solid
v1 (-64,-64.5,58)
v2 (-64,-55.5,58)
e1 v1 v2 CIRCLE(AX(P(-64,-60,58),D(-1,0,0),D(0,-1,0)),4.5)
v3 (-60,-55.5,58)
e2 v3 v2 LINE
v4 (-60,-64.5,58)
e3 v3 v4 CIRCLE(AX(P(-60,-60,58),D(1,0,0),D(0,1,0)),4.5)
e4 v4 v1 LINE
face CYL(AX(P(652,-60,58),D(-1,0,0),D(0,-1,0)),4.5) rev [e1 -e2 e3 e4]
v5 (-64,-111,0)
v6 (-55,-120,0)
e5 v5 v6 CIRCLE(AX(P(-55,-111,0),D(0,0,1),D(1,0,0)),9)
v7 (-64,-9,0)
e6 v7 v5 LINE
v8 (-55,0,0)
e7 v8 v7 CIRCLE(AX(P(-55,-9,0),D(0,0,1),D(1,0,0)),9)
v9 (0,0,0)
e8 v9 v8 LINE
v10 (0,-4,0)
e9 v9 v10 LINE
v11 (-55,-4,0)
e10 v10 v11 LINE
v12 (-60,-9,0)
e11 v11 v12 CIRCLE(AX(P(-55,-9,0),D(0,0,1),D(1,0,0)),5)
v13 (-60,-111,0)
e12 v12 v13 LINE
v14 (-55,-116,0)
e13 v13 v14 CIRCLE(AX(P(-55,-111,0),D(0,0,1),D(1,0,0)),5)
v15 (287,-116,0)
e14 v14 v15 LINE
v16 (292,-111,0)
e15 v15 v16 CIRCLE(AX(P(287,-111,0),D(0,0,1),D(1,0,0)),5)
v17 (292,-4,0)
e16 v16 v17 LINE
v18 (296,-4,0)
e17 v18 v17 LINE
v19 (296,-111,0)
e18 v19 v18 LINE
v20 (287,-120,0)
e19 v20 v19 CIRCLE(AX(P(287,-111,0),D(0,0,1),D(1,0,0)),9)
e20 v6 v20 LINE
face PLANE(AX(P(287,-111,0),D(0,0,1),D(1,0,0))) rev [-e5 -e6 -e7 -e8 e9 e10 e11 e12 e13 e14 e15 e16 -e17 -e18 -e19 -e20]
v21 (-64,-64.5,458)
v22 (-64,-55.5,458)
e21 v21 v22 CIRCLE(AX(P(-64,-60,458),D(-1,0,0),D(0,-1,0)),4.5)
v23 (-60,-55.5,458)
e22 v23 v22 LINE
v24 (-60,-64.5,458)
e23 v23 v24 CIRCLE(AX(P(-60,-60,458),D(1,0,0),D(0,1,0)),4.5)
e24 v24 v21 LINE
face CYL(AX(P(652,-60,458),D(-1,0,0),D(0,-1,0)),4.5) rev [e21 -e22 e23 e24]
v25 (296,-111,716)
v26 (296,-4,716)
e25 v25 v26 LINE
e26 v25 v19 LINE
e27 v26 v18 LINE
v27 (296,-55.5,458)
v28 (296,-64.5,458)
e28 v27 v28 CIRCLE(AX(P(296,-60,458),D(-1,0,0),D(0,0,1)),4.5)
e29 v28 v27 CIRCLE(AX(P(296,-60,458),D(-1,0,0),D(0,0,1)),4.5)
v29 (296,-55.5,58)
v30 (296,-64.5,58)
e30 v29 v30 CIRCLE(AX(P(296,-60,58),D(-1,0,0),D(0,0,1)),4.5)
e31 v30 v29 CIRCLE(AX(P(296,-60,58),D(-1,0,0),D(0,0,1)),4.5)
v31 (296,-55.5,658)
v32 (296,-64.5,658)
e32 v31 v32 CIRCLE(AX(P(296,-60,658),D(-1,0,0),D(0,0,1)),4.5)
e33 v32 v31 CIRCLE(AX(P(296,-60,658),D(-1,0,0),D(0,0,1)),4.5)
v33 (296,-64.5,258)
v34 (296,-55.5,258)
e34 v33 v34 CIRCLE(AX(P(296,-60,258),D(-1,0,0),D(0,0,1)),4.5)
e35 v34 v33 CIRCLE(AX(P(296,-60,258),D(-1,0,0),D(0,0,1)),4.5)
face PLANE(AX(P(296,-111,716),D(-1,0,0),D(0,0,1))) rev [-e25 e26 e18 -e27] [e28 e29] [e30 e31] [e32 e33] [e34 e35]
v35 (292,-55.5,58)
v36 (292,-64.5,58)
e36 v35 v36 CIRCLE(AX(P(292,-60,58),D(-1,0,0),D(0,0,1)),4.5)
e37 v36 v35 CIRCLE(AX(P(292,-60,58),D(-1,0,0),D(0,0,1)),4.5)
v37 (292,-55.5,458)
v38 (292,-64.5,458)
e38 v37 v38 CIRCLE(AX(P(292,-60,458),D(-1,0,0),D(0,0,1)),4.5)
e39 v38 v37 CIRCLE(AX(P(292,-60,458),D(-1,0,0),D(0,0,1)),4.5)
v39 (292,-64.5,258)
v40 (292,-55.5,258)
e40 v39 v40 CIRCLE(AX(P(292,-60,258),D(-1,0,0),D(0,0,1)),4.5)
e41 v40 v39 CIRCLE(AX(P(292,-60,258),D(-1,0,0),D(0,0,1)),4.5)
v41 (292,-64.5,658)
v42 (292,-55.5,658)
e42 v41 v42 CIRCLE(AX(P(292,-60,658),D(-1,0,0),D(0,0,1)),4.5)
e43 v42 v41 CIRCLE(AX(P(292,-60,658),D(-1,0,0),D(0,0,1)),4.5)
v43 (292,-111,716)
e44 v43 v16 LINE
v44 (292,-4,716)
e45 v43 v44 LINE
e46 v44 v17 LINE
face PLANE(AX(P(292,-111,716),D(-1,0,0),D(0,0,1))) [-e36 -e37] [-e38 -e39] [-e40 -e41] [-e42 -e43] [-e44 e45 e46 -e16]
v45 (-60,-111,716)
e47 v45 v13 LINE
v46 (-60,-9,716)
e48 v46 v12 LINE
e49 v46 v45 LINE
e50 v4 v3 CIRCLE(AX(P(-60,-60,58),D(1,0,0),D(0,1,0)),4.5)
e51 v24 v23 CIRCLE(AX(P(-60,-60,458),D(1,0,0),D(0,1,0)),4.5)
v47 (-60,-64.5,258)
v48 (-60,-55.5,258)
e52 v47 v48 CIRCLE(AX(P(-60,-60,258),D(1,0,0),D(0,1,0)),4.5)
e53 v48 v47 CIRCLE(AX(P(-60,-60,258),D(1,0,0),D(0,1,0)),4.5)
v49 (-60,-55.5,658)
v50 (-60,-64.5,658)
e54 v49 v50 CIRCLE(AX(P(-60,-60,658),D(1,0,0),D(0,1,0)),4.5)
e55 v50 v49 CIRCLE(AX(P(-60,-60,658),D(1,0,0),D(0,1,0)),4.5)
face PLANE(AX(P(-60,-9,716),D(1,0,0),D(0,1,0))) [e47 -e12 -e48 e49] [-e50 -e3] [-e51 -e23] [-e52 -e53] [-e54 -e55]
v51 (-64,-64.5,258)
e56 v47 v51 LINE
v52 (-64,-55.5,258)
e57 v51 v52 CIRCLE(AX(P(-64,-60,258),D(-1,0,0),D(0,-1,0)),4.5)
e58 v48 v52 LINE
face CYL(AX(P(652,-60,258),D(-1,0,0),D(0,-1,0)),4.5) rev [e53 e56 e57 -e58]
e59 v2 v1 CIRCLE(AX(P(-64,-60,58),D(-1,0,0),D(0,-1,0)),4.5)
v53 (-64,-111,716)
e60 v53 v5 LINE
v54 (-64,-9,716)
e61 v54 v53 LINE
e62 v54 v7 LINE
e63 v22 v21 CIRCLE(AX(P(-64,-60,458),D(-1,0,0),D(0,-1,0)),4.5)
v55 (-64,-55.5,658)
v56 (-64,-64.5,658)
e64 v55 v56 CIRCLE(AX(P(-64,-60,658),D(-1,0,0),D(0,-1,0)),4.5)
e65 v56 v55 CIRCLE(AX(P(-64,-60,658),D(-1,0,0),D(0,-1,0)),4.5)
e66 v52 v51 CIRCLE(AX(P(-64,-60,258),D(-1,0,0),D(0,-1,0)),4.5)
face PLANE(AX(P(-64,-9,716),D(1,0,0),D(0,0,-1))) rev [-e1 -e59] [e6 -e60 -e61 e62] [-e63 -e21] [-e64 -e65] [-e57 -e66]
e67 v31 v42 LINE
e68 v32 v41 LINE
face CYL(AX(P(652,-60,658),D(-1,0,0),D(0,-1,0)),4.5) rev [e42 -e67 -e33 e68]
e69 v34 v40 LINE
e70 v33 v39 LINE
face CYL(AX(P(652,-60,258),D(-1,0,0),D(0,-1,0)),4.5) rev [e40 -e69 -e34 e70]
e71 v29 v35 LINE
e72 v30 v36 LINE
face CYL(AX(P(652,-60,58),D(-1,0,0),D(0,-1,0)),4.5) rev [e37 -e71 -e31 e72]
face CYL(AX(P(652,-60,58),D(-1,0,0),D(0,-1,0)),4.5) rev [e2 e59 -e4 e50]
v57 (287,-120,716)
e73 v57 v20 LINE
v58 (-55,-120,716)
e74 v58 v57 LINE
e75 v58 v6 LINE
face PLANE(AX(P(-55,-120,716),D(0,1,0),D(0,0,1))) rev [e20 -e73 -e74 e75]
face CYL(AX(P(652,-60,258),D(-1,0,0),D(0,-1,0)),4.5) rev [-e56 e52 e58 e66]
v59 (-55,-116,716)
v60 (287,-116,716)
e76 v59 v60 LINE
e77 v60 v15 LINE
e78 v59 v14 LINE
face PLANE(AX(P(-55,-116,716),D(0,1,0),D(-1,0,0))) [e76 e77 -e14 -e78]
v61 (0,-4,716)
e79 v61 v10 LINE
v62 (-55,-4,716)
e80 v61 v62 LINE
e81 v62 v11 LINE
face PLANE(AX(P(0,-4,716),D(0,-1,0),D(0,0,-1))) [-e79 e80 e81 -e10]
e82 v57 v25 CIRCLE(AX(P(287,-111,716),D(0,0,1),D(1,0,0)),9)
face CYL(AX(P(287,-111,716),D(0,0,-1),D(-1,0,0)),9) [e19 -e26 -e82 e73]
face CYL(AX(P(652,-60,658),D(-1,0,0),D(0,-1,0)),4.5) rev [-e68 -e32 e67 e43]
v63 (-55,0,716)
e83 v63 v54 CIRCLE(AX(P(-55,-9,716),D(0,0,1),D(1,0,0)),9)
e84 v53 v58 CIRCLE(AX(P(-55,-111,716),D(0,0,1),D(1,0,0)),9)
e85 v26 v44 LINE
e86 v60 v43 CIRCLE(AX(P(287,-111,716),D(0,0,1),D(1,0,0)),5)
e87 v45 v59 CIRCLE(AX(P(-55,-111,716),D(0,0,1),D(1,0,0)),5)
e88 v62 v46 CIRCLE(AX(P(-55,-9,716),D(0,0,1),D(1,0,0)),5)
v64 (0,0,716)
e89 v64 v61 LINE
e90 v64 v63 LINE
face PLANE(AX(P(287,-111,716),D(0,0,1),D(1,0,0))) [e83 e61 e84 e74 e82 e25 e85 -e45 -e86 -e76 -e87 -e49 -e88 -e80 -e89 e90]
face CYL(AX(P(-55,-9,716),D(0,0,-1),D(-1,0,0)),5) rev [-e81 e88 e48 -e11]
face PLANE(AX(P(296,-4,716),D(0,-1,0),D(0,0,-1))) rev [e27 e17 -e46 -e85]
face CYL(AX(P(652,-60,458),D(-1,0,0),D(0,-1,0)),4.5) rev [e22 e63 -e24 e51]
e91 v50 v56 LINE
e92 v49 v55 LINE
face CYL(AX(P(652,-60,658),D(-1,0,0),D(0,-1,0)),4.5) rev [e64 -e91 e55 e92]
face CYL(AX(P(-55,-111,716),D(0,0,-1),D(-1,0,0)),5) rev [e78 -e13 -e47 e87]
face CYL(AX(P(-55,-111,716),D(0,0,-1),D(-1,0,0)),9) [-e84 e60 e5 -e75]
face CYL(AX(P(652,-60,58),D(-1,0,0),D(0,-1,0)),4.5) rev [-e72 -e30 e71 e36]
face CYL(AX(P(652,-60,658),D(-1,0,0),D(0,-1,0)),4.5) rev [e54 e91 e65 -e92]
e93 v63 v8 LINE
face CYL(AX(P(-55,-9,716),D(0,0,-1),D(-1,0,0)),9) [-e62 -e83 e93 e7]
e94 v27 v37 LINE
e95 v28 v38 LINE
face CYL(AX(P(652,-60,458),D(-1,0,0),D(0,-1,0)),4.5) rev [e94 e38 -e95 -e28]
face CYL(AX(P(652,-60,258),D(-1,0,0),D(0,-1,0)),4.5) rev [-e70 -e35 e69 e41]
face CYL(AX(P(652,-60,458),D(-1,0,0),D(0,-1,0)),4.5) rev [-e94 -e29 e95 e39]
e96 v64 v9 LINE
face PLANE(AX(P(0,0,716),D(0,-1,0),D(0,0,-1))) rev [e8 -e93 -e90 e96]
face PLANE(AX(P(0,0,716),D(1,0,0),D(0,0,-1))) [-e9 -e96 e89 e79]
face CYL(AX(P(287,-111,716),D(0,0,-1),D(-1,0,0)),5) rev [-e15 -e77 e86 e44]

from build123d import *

# Parameters (mm, degrees)
BOSS_EXTRUDE1_DEPTH = 716
SKETCH2_R           = 4.5
CUT_EXTRUDE1_DEPTH  = 716


with BuildPart() as part:
    # Sketch1 → Boss-Extrude1 (new body)
    with BuildSketch(Plane.XY):
        with BuildLine():
            Line((0, 0), (-55, 0))
            ThreePointArc((-55, 0), (-61.363961031, -2.636038969), (-64, -9))
            Line((-64, -9), (-64, -111))
            ThreePointArc((-64, -111), (-61.363961031, -117.363961031), (-55, -120))
            Line((-55, -120), (287, -120))
            ThreePointArc((287, -120), (293.363961031, -117.363961031), (296, -111))
            Line((296, -111), (296, -4))
            Line((296, -4), (292, -4))
            Line((292, -4), (292, -111))
            ThreePointArc((292, -111), (290.535533906, -114.535533906), (287, -116))
            Line((287, -116), (-55, -116))
            ThreePointArc((-55, -116), (-58.535533906, -114.535533906), (-60, -111))
            Line((-60, -111), (-60, -9))
            ThreePointArc((-60, -9), (-58.535533906, -5.464466094), (-55, -4))
            Line((-55, -4), (0, -4))
            Line((0, -4), (0, 0))
        make_face()
    extrude(amount=BOSS_EXTRUDE1_DEPTH)

    # Sketch2 → Cut-Extrude1 (cut)
    with BuildSketch(Plane.ZY.offset(64)):
        with Locations(Location((58, -60, 0), (0, 0, 270))):
            Circle(SKETCH2_R)
        with Locations(Location((258, -60, 0), (0, 0, 270))):
            Circle(SKETCH2_R)
        with Locations(Location((458, -60, 0), (0, 0, 270))):
            Circle(SKETCH2_R)
        with Locations(Location((658, -60, 0), (0, 0, 270))):
            Circle(SKETCH2_R)
    extrude(amount=-CUT_EXTRUDE1_DEPTH, mode=Mode.SUBTRACT)


solid = part.part
